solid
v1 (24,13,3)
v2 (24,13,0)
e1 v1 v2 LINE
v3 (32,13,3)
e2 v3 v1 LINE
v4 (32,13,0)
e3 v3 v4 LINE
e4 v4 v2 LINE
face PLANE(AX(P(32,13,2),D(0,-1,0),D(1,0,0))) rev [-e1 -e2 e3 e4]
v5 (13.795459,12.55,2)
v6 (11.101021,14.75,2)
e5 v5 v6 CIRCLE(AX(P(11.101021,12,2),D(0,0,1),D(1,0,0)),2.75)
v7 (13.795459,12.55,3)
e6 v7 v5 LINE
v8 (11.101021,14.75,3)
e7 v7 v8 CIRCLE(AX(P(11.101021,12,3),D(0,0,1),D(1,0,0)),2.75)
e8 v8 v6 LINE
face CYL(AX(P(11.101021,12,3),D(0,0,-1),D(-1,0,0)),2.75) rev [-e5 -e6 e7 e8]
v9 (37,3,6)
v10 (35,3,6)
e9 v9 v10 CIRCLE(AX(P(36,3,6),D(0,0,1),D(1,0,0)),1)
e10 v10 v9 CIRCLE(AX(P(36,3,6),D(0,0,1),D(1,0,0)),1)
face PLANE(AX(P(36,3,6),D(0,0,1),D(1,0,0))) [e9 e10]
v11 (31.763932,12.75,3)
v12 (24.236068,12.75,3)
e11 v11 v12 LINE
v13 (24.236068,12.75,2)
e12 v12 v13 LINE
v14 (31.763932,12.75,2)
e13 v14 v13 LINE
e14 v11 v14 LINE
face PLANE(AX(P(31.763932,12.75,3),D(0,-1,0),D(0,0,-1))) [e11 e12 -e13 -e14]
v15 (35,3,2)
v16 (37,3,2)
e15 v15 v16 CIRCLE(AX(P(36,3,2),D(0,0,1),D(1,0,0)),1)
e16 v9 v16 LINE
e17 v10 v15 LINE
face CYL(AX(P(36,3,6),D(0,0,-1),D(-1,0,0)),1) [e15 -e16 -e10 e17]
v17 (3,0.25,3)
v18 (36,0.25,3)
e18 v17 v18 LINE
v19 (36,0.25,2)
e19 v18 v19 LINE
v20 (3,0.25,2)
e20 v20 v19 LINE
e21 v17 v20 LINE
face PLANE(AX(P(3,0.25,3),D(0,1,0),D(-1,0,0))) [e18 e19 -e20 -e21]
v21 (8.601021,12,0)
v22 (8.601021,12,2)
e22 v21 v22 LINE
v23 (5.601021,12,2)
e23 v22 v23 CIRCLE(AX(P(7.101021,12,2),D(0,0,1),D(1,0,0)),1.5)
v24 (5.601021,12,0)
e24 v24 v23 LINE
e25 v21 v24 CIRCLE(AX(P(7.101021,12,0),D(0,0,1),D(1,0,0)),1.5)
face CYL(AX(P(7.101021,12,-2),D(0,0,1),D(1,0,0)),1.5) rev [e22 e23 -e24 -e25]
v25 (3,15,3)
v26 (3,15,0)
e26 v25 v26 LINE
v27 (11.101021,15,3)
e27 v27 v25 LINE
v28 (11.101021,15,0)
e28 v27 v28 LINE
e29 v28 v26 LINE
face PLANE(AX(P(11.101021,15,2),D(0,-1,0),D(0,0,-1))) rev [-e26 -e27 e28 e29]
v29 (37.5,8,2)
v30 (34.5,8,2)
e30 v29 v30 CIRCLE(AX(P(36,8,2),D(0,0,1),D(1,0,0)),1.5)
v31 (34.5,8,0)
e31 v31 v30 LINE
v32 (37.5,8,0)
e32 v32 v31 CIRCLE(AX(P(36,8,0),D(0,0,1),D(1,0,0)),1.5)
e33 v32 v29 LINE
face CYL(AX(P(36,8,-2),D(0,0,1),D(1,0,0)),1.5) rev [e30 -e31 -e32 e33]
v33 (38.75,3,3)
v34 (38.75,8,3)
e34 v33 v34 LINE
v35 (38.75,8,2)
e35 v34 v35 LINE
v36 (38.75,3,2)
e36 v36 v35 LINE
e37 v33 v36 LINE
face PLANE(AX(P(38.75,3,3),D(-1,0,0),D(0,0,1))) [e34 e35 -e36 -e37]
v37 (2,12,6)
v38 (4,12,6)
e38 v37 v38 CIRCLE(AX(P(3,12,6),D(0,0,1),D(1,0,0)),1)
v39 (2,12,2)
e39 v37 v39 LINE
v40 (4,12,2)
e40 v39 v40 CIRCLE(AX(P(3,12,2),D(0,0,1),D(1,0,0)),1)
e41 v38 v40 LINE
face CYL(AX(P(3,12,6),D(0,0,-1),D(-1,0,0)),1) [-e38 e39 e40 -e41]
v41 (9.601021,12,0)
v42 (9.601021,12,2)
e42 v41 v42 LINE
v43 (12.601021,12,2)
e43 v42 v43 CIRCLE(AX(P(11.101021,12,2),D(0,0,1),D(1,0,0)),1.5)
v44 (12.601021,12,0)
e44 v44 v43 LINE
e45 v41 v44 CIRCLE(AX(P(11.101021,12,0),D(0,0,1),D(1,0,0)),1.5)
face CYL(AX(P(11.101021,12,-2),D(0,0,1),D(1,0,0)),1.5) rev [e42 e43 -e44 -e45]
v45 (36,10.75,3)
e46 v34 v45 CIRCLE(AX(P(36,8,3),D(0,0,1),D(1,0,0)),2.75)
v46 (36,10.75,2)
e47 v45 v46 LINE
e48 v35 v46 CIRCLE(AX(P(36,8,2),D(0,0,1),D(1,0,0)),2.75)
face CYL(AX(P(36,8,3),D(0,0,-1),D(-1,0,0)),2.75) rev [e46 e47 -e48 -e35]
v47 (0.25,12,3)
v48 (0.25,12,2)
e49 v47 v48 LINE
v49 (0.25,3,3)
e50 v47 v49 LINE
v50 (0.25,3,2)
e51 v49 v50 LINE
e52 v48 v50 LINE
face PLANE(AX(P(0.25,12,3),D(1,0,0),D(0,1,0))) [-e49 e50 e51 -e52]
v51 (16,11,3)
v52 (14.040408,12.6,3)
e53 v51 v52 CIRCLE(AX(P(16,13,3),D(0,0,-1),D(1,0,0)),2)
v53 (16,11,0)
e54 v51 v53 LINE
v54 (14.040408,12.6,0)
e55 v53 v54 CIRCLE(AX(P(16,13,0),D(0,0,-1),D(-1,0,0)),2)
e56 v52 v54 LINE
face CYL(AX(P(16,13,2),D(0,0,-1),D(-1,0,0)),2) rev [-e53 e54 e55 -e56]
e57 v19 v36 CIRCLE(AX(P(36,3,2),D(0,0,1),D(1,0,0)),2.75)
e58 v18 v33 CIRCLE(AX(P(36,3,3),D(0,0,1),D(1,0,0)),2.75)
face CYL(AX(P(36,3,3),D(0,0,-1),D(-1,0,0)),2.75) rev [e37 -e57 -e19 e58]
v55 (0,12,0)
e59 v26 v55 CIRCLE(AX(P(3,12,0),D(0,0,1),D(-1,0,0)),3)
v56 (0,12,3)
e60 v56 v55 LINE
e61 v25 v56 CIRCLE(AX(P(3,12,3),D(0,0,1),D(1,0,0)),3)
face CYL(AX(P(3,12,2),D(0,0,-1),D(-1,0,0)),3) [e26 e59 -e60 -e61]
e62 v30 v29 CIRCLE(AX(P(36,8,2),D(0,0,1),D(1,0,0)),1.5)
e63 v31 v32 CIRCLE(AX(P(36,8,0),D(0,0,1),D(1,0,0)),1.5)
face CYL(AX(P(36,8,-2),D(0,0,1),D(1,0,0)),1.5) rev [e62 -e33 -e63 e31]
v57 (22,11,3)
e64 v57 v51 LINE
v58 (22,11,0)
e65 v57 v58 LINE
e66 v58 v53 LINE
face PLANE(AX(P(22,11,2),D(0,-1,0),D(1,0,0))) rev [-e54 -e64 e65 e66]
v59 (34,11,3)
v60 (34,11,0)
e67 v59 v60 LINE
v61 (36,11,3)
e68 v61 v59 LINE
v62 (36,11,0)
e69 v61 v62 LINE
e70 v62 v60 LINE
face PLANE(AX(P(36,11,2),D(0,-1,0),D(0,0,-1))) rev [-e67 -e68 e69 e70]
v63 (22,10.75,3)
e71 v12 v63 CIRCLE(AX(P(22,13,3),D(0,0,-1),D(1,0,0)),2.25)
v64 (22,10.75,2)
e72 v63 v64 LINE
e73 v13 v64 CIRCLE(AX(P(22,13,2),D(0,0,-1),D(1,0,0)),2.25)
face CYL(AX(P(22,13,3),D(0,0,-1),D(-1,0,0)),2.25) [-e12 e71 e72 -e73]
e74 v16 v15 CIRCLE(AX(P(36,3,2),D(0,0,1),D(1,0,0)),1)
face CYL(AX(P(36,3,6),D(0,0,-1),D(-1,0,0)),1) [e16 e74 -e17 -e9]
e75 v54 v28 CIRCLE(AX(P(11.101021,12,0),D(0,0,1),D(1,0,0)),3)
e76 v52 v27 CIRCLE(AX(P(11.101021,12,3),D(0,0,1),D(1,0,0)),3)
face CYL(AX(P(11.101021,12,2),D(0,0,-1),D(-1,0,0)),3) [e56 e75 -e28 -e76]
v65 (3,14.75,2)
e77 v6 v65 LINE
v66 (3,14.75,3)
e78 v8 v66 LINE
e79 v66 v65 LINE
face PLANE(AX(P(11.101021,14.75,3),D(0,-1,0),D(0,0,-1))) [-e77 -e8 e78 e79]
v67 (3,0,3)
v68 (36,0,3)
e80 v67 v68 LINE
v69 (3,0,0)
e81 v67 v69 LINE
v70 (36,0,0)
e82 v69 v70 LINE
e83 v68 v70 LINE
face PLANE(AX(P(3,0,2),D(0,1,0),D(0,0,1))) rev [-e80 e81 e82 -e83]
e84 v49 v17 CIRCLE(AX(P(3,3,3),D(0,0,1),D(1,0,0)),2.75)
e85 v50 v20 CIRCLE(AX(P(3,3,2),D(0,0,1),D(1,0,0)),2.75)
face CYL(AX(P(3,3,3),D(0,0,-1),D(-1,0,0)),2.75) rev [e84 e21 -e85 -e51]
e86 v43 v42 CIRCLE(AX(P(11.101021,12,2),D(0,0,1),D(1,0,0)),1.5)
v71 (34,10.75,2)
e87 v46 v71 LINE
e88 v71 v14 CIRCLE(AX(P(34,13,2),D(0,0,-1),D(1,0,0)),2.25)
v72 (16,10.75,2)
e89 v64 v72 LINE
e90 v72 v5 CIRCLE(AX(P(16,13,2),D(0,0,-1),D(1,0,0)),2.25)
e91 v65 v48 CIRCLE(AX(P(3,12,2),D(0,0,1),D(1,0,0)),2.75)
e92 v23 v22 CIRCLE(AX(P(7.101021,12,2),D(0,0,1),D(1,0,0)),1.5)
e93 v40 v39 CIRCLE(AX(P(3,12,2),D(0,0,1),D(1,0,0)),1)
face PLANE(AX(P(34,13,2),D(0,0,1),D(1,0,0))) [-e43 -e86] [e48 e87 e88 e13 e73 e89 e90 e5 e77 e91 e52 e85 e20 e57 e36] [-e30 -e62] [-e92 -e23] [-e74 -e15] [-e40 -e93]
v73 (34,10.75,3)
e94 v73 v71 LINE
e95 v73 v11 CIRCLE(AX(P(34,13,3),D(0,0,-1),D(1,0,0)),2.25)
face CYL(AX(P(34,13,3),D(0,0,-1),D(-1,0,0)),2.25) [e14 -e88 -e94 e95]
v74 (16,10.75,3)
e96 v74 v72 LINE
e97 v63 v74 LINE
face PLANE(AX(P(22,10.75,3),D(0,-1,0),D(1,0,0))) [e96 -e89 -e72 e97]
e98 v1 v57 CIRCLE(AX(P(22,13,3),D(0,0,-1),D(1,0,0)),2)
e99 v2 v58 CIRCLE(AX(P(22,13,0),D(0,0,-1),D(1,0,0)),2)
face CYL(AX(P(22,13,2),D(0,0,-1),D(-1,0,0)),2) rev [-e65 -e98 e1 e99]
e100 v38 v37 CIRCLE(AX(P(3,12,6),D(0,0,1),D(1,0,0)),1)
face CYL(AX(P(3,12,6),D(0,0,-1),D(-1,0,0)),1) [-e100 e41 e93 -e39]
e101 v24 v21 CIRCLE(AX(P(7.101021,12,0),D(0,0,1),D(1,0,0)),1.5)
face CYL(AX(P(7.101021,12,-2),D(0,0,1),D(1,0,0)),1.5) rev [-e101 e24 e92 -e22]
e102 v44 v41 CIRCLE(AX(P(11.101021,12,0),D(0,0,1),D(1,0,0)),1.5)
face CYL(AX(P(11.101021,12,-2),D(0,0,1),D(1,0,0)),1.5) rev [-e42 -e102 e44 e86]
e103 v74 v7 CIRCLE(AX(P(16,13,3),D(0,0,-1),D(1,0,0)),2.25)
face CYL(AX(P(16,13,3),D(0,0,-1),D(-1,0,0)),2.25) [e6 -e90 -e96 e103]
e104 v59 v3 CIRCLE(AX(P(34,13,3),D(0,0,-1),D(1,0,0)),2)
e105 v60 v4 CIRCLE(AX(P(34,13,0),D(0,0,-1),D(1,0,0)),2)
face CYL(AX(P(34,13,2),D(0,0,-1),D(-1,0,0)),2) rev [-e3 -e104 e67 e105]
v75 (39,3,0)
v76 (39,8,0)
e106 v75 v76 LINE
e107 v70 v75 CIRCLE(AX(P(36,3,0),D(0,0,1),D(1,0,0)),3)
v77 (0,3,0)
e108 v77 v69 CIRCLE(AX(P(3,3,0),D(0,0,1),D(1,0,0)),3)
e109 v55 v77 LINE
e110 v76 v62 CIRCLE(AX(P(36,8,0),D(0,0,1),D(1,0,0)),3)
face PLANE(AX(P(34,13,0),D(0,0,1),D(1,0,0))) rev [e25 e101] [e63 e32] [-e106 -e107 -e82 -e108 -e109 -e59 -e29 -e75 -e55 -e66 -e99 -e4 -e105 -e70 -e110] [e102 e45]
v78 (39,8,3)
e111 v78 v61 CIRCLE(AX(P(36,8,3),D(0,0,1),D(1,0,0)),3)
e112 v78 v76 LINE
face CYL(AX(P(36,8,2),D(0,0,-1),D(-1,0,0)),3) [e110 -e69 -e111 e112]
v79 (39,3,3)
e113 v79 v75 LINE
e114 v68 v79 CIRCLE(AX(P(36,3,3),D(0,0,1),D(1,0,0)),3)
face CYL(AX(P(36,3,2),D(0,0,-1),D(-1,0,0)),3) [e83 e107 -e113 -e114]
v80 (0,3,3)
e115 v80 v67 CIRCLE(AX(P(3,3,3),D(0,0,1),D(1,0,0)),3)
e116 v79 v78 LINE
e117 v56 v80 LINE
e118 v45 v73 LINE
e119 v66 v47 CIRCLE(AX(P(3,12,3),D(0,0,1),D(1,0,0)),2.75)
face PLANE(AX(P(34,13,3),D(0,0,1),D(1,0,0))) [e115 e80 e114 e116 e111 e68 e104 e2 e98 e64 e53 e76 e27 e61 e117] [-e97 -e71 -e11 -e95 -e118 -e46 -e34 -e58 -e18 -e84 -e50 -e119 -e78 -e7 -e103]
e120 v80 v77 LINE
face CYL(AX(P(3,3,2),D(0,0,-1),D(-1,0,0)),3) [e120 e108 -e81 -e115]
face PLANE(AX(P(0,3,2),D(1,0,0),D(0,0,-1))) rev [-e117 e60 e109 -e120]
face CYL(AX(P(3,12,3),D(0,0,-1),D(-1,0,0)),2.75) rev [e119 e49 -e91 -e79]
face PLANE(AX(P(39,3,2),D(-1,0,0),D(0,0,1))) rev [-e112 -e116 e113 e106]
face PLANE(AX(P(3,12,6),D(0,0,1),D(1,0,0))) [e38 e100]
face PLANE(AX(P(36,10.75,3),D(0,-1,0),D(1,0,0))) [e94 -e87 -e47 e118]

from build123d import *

# Parameters (mm, degrees)
BASE_PLATE_DEPTH         = 2
PERIMETER_RIM_DEPTH      = 1
PIN_1_SKETCH_R           = 1
PIN_1_2_DEPTH            = 4
PIN_2_SKETCH_R           = 1
PIN_2_2_DEPTH            = 4
THROUGH_HOLES_SKETCH_R   = 1.5
THROUGH_HOLES_3X_3_DEPTH = 4


with BuildPart() as part:
    # Base Plate Sketch → Base Plate (new body)
    with BuildSketch(Plane.XY):
        with BuildLine():
            Line((0, 3), (0, 12))
            ThreePointArc((0, 12), (0.878679656, 14.121320344), (3, 15))
            Line((3, 15), (11.101020514, 15))
            ThreePointArc((11.101020514, 15), (12.998387111, 14.323790008), (14.040408206, 12.6))
            ThreePointArc((14.040408206, 12.6), (14.735088936, 11.450806662), (16, 11))
            Line((16, 11), (22, 11))
            ThreePointArc((22, 11), (23.414213562, 11.585786438), (24, 13))
            Line((24, 13), (32, 13))
            ThreePointArc((32, 13), (32.585786438, 11.585786438), (34, 11))
            Line((34, 11), (36, 11))
            ThreePointArc((36, 11), (38.121320344, 10.121320344), (39, 8))
            Line((39, 8), (39, 3))
            ThreePointArc((39, 3), (38.121320344, 0.878679656), (36, 0))
            Line((36, 0), (3, 0))
            ThreePointArc((3, 0), (0.878679656, 0.878679656), (0, 3))
        make_face()
    extrude(amount=BASE_PLATE_DEPTH)

    # Perimeter Rim Sketch → Perimeter Rim (add)
    with BuildSketch(Plane.XY.offset(2)):
        with BuildLine():
            Line((32, 13), (24, 13))
            ThreePointArc((24, 13), (23.414213562, 11.585786438), (22, 11))
            Line((22, 11), (16, 11))
            ThreePointArc((16, 11), (14.735088936, 11.450806662), (14.040408206, 12.6))
            ThreePointArc((14.040408206, 12.6), (12.998387111, 14.323790008), (11.101020514, 15))
            Line((11.101020514, 15), (3, 15))
            ThreePointArc((3, 15), (0.878679656, 14.121320344), (0, 12))
            Line((0, 12), (0, 3))
            ThreePointArc((0, 3), (0.878679656, 0.878679656), (3, 0))
            Line((3, 0), (36, 0))
            ThreePointArc((36, 0), (38.121320344, 0.878679656), (39, 3))
            Line((39, 3), (39, 8))
            ThreePointArc((39, 8), (38.121320344, 10.121320344), (36, 11))
            Line((36, 11), (34, 11))
            ThreePointArc((34, 11), (32.585786438, 11.585786438), (32, 13))
        make_face()
        with BuildLine():
            Line((31.763932023, 12.75), (24.236067977, 12.75))
            ThreePointArc((24.236067977, 12.75), (23.5, 11.322949017), (22, 10.75))
            Line((22, 10.75), (16, 10.75))
            ThreePointArc((16, 10.75), (14.576975053, 11.257157494), (13.795459231, 12.55))
            ThreePointArc((13.795459231, 12.55), (12.840273228, 14.13014084), (11.101020514, 14.75))
            Line((11.101020514, 14.75), (3, 14.75))
            ThreePointArc((3, 14.75), (1.055456352, 13.944543648), (0.25, 12))
            Line((0.25, 12), (0.25, 3))
            ThreePointArc((0.25, 3), (1.055456352, 1.055456352), (3, 0.25))
            Line((3, 0.25), (36, 0.25))
            ThreePointArc((36, 0.25), (37.944543648, 1.055456352), (38.75, 3))
            Line((38.75, 3), (38.75, 8))
            ThreePointArc((38.75, 8), (37.944543648, 9.944543648), (36, 10.75))
            Line((36, 10.75), (34, 10.75))
            ThreePointArc((34, 10.75), (32.5, 11.322949017), (31.763932023, 12.75))
        make_face(mode=Mode.SUBTRACT)
    extrude(amount=PERIMETER_RIM_DEPTH)

    # Pin 1 Sketch → Pin 1 Ø2 (add)
    with BuildSketch(Plane.XY.offset(2)):
        with Locations((36, 3)):
            Circle(PIN_1_SKETCH_R)
    extrude(amount=PIN_1_2_DEPTH)

    # Pin 2 Sketch → Pin 2 Ø2 (add)
    with BuildSketch(Plane.XY.offset(2)):
        with Locations((3, 12)):
            Circle(PIN_2_SKETCH_R)
    extrude(amount=PIN_2_2_DEPTH)

    # Through Holes Sketch → Through Holes 3xØ3 (cut)
    with BuildSketch(Plane.XY.offset(2)):
        with Locations((36, 8)):
            Circle(THROUGH_HOLES_SKETCH_R)
        with Locations((11.101020514, 12)):
            Circle(THROUGH_HOLES_SKETCH_R)
        with Locations((7.101020514, 12)):
            Circle(THROUGH_HOLES_SKETCH_R)
    extrude(amount=-THROUGH_HOLES_3X_3_DEPTH, mode=Mode.SUBTRACT)


solid = part.part
